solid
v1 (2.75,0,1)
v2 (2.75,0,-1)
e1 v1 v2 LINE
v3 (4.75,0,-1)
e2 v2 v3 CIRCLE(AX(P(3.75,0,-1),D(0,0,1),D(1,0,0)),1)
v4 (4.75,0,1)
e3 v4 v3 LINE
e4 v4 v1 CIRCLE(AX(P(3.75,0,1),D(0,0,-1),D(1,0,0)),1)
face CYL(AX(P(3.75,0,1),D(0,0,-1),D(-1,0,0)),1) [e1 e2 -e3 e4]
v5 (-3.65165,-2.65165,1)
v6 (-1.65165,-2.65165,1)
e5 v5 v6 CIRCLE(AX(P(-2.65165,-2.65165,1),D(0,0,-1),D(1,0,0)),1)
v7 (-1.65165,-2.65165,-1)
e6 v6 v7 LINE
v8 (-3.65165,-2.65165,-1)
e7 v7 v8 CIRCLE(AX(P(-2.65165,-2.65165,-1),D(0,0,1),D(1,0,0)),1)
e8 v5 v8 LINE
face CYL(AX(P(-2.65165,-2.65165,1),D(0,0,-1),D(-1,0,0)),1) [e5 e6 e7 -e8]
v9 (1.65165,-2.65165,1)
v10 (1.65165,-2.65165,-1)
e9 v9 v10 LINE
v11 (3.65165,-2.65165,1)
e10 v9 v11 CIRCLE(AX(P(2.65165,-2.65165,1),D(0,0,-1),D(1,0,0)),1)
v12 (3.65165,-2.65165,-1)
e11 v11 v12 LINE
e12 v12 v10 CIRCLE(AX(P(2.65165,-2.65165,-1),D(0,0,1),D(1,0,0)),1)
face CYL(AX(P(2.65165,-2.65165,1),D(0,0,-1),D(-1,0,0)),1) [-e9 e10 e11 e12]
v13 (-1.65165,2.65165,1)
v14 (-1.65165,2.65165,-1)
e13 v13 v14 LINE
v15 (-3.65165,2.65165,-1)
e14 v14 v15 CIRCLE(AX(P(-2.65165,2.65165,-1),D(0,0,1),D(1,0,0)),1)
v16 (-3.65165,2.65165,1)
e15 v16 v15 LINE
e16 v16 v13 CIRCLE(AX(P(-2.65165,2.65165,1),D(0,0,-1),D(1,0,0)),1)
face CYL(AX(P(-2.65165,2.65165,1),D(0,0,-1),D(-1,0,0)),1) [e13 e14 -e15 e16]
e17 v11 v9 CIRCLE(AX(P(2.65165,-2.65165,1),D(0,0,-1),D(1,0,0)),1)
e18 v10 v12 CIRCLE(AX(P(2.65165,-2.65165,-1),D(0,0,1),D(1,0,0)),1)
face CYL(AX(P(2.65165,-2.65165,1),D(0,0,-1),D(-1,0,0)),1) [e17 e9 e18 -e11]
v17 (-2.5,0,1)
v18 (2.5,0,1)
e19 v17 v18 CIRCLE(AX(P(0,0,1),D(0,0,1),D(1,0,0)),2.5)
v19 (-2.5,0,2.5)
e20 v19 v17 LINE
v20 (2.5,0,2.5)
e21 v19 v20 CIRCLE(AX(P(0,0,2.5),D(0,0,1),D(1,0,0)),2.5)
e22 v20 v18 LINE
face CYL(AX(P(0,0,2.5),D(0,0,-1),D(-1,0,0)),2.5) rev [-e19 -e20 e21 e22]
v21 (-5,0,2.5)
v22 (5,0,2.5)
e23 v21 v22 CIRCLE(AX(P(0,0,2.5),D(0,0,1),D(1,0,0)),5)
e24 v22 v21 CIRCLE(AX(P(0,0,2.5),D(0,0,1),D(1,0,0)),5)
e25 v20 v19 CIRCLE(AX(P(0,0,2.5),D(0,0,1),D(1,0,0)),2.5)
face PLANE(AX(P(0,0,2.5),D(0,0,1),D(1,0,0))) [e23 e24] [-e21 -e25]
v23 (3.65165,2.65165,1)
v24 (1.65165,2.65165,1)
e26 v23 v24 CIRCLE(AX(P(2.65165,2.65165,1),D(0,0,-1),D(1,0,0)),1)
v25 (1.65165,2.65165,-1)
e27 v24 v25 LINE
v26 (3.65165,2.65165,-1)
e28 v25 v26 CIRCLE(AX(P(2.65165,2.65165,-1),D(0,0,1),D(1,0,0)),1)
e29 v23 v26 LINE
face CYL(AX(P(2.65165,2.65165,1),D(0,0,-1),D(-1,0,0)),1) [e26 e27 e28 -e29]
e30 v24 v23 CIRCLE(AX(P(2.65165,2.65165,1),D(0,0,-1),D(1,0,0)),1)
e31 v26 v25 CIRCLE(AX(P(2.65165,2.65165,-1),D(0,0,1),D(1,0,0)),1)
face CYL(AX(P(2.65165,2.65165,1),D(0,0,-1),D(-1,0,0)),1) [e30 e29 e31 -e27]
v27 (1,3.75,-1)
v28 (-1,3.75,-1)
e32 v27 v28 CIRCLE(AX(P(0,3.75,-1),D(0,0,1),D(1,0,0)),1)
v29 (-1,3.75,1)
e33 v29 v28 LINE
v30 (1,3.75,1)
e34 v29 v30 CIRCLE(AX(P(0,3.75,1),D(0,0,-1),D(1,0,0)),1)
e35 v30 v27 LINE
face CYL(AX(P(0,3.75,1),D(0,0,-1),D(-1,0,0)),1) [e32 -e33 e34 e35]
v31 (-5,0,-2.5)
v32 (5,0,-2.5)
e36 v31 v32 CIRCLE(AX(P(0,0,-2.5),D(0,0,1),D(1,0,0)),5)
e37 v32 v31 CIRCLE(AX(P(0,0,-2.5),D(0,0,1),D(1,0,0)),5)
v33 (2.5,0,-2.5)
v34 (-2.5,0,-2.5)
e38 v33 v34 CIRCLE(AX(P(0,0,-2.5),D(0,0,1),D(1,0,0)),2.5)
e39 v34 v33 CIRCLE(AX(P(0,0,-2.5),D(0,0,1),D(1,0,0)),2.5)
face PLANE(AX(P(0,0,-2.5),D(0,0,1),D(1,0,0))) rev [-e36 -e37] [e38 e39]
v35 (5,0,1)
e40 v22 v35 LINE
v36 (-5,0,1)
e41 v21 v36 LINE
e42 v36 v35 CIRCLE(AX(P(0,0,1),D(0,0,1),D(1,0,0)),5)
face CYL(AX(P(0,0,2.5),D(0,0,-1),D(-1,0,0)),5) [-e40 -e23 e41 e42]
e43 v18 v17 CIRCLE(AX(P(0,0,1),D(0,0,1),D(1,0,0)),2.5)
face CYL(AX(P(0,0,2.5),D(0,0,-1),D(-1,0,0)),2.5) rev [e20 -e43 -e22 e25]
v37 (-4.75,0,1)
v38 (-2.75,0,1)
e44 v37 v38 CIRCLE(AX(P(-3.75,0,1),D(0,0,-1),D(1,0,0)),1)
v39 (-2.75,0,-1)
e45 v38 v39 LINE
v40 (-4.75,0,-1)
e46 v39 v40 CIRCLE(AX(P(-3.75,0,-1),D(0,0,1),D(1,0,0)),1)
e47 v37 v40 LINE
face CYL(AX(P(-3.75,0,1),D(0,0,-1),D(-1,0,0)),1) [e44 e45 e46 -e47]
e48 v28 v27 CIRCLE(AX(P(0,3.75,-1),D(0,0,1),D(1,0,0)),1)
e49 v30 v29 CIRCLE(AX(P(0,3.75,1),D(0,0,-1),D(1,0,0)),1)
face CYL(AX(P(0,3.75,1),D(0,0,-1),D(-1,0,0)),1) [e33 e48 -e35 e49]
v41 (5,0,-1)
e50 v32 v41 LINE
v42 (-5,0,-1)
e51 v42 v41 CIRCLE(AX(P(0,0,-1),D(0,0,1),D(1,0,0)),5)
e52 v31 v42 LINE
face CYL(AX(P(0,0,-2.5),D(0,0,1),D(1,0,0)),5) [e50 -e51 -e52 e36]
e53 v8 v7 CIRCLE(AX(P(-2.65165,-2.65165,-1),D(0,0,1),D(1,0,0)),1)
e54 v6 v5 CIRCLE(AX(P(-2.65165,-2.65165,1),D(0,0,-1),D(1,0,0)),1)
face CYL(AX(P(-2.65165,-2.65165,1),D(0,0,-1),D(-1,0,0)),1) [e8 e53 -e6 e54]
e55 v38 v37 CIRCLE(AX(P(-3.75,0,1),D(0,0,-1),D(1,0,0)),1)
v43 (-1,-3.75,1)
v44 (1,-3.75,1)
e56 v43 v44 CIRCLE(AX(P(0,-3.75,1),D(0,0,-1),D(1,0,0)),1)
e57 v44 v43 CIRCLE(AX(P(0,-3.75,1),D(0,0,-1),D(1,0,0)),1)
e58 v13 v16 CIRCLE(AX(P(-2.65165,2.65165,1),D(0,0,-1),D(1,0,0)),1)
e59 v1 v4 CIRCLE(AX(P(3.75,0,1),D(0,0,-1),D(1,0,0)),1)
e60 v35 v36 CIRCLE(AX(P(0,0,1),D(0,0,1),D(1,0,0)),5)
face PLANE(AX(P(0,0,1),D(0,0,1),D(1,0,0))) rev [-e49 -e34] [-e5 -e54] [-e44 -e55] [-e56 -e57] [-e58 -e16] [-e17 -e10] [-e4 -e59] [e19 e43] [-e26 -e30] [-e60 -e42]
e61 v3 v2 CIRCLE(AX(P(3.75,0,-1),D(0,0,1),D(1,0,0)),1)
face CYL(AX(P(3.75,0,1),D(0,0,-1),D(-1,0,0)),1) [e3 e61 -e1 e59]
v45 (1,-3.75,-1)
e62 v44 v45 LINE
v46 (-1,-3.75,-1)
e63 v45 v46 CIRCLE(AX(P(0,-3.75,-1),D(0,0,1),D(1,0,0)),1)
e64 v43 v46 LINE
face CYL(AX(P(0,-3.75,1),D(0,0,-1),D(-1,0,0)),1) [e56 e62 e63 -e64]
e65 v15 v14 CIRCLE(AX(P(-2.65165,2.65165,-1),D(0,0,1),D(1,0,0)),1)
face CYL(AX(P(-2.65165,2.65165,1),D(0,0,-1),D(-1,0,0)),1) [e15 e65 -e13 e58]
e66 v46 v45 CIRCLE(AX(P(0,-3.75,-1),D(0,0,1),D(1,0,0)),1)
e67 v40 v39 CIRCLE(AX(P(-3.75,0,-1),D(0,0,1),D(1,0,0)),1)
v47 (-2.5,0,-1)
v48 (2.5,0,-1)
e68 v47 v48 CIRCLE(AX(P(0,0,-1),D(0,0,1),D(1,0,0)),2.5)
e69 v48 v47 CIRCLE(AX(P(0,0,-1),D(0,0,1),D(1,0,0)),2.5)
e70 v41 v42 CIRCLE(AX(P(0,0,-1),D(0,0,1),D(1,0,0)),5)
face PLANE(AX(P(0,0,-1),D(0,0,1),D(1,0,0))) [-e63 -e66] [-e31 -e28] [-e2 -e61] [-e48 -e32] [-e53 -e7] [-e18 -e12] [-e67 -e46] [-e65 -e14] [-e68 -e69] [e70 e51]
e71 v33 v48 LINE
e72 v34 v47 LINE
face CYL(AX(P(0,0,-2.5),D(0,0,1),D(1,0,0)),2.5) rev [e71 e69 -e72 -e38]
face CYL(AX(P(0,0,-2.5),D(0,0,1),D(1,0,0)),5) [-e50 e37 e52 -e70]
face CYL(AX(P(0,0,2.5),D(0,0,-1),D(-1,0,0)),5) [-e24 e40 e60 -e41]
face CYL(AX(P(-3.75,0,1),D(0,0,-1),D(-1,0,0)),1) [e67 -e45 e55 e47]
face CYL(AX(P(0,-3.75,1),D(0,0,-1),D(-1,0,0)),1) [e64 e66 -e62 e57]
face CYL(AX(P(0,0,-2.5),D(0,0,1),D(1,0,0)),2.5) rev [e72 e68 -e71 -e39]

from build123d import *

# Parameters (mm, degrees)
BOSS_EXTRUDE1_START = 1
SKETCH4_4_R         = 5
SKETCH4_4_R_2       = 2.5
BOSS_EXTRUDE1_DEPTH = 1.5
BOSS_EXTRUDE2_START = -1
SKETCH_4_4_R        = 5
SKETCH_4_4_R_2      = 2.5
BOSS_EXTRUDE2_DEPTH = 1.5
SKETCH8_R           = 1
BOSS_EXTRUDE3_DEPTH = 2


with BuildPart() as part:
    # Sketch4<4> → Boss-Extrude1 (new body)
    with BuildSketch(Plane.XY.offset(BOSS_EXTRUDE1_START)):
        Circle(SKETCH4_4_R)
        Circle(SKETCH4_4_R_2, mode=Mode.SUBTRACT)
    extrude(amount=BOSS_EXTRUDE1_DEPTH)



with BuildPart() as body_2:
    # 草图4<4> → Boss-Extrude2 (new body)
    with BuildSketch(Plane.XY.offset(BOSS_EXTRUDE2_START)):
        Circle(SKETCH_4_4_R)
        Circle(SKETCH_4_4_R_2, mode=Mode.SUBTRACT)
    extrude(amount=-BOSS_EXTRUDE2_DEPTH)


with BuildPart() as part_1:
    add(part.part)

    add(body_2.part)  # Boss-Extrude3 merges body 2
    # Sketch8 → Boss-Extrude3 (add)
    with BuildSketch(Plane.XY.offset(-1)):
        with Locations((0, 3.75)):
            Circle(SKETCH8_R)
        with Locations((2.651650429, 2.651650429)):
            Circle(SKETCH8_R)
        with Locations((3.75, 0)):
            Circle(SKETCH8_R)
        with Locations((2.651650429, -2.651650429)):
            Circle(SKETCH8_R)
        with Locations((0, -3.75)):
            Circle(SKETCH8_R)
        with Locations((-2.651650429, -2.651650429)):
            Circle(SKETCH8_R)
        with Locations((-3.75, 0)):
            Circle(SKETCH8_R)
        with Locations((-2.651650429, 2.651650429)):
            Circle(SKETCH8_R)
    extrude(amount=BOSS_EXTRUDE3_DEPTH)


solid = part_1.part
